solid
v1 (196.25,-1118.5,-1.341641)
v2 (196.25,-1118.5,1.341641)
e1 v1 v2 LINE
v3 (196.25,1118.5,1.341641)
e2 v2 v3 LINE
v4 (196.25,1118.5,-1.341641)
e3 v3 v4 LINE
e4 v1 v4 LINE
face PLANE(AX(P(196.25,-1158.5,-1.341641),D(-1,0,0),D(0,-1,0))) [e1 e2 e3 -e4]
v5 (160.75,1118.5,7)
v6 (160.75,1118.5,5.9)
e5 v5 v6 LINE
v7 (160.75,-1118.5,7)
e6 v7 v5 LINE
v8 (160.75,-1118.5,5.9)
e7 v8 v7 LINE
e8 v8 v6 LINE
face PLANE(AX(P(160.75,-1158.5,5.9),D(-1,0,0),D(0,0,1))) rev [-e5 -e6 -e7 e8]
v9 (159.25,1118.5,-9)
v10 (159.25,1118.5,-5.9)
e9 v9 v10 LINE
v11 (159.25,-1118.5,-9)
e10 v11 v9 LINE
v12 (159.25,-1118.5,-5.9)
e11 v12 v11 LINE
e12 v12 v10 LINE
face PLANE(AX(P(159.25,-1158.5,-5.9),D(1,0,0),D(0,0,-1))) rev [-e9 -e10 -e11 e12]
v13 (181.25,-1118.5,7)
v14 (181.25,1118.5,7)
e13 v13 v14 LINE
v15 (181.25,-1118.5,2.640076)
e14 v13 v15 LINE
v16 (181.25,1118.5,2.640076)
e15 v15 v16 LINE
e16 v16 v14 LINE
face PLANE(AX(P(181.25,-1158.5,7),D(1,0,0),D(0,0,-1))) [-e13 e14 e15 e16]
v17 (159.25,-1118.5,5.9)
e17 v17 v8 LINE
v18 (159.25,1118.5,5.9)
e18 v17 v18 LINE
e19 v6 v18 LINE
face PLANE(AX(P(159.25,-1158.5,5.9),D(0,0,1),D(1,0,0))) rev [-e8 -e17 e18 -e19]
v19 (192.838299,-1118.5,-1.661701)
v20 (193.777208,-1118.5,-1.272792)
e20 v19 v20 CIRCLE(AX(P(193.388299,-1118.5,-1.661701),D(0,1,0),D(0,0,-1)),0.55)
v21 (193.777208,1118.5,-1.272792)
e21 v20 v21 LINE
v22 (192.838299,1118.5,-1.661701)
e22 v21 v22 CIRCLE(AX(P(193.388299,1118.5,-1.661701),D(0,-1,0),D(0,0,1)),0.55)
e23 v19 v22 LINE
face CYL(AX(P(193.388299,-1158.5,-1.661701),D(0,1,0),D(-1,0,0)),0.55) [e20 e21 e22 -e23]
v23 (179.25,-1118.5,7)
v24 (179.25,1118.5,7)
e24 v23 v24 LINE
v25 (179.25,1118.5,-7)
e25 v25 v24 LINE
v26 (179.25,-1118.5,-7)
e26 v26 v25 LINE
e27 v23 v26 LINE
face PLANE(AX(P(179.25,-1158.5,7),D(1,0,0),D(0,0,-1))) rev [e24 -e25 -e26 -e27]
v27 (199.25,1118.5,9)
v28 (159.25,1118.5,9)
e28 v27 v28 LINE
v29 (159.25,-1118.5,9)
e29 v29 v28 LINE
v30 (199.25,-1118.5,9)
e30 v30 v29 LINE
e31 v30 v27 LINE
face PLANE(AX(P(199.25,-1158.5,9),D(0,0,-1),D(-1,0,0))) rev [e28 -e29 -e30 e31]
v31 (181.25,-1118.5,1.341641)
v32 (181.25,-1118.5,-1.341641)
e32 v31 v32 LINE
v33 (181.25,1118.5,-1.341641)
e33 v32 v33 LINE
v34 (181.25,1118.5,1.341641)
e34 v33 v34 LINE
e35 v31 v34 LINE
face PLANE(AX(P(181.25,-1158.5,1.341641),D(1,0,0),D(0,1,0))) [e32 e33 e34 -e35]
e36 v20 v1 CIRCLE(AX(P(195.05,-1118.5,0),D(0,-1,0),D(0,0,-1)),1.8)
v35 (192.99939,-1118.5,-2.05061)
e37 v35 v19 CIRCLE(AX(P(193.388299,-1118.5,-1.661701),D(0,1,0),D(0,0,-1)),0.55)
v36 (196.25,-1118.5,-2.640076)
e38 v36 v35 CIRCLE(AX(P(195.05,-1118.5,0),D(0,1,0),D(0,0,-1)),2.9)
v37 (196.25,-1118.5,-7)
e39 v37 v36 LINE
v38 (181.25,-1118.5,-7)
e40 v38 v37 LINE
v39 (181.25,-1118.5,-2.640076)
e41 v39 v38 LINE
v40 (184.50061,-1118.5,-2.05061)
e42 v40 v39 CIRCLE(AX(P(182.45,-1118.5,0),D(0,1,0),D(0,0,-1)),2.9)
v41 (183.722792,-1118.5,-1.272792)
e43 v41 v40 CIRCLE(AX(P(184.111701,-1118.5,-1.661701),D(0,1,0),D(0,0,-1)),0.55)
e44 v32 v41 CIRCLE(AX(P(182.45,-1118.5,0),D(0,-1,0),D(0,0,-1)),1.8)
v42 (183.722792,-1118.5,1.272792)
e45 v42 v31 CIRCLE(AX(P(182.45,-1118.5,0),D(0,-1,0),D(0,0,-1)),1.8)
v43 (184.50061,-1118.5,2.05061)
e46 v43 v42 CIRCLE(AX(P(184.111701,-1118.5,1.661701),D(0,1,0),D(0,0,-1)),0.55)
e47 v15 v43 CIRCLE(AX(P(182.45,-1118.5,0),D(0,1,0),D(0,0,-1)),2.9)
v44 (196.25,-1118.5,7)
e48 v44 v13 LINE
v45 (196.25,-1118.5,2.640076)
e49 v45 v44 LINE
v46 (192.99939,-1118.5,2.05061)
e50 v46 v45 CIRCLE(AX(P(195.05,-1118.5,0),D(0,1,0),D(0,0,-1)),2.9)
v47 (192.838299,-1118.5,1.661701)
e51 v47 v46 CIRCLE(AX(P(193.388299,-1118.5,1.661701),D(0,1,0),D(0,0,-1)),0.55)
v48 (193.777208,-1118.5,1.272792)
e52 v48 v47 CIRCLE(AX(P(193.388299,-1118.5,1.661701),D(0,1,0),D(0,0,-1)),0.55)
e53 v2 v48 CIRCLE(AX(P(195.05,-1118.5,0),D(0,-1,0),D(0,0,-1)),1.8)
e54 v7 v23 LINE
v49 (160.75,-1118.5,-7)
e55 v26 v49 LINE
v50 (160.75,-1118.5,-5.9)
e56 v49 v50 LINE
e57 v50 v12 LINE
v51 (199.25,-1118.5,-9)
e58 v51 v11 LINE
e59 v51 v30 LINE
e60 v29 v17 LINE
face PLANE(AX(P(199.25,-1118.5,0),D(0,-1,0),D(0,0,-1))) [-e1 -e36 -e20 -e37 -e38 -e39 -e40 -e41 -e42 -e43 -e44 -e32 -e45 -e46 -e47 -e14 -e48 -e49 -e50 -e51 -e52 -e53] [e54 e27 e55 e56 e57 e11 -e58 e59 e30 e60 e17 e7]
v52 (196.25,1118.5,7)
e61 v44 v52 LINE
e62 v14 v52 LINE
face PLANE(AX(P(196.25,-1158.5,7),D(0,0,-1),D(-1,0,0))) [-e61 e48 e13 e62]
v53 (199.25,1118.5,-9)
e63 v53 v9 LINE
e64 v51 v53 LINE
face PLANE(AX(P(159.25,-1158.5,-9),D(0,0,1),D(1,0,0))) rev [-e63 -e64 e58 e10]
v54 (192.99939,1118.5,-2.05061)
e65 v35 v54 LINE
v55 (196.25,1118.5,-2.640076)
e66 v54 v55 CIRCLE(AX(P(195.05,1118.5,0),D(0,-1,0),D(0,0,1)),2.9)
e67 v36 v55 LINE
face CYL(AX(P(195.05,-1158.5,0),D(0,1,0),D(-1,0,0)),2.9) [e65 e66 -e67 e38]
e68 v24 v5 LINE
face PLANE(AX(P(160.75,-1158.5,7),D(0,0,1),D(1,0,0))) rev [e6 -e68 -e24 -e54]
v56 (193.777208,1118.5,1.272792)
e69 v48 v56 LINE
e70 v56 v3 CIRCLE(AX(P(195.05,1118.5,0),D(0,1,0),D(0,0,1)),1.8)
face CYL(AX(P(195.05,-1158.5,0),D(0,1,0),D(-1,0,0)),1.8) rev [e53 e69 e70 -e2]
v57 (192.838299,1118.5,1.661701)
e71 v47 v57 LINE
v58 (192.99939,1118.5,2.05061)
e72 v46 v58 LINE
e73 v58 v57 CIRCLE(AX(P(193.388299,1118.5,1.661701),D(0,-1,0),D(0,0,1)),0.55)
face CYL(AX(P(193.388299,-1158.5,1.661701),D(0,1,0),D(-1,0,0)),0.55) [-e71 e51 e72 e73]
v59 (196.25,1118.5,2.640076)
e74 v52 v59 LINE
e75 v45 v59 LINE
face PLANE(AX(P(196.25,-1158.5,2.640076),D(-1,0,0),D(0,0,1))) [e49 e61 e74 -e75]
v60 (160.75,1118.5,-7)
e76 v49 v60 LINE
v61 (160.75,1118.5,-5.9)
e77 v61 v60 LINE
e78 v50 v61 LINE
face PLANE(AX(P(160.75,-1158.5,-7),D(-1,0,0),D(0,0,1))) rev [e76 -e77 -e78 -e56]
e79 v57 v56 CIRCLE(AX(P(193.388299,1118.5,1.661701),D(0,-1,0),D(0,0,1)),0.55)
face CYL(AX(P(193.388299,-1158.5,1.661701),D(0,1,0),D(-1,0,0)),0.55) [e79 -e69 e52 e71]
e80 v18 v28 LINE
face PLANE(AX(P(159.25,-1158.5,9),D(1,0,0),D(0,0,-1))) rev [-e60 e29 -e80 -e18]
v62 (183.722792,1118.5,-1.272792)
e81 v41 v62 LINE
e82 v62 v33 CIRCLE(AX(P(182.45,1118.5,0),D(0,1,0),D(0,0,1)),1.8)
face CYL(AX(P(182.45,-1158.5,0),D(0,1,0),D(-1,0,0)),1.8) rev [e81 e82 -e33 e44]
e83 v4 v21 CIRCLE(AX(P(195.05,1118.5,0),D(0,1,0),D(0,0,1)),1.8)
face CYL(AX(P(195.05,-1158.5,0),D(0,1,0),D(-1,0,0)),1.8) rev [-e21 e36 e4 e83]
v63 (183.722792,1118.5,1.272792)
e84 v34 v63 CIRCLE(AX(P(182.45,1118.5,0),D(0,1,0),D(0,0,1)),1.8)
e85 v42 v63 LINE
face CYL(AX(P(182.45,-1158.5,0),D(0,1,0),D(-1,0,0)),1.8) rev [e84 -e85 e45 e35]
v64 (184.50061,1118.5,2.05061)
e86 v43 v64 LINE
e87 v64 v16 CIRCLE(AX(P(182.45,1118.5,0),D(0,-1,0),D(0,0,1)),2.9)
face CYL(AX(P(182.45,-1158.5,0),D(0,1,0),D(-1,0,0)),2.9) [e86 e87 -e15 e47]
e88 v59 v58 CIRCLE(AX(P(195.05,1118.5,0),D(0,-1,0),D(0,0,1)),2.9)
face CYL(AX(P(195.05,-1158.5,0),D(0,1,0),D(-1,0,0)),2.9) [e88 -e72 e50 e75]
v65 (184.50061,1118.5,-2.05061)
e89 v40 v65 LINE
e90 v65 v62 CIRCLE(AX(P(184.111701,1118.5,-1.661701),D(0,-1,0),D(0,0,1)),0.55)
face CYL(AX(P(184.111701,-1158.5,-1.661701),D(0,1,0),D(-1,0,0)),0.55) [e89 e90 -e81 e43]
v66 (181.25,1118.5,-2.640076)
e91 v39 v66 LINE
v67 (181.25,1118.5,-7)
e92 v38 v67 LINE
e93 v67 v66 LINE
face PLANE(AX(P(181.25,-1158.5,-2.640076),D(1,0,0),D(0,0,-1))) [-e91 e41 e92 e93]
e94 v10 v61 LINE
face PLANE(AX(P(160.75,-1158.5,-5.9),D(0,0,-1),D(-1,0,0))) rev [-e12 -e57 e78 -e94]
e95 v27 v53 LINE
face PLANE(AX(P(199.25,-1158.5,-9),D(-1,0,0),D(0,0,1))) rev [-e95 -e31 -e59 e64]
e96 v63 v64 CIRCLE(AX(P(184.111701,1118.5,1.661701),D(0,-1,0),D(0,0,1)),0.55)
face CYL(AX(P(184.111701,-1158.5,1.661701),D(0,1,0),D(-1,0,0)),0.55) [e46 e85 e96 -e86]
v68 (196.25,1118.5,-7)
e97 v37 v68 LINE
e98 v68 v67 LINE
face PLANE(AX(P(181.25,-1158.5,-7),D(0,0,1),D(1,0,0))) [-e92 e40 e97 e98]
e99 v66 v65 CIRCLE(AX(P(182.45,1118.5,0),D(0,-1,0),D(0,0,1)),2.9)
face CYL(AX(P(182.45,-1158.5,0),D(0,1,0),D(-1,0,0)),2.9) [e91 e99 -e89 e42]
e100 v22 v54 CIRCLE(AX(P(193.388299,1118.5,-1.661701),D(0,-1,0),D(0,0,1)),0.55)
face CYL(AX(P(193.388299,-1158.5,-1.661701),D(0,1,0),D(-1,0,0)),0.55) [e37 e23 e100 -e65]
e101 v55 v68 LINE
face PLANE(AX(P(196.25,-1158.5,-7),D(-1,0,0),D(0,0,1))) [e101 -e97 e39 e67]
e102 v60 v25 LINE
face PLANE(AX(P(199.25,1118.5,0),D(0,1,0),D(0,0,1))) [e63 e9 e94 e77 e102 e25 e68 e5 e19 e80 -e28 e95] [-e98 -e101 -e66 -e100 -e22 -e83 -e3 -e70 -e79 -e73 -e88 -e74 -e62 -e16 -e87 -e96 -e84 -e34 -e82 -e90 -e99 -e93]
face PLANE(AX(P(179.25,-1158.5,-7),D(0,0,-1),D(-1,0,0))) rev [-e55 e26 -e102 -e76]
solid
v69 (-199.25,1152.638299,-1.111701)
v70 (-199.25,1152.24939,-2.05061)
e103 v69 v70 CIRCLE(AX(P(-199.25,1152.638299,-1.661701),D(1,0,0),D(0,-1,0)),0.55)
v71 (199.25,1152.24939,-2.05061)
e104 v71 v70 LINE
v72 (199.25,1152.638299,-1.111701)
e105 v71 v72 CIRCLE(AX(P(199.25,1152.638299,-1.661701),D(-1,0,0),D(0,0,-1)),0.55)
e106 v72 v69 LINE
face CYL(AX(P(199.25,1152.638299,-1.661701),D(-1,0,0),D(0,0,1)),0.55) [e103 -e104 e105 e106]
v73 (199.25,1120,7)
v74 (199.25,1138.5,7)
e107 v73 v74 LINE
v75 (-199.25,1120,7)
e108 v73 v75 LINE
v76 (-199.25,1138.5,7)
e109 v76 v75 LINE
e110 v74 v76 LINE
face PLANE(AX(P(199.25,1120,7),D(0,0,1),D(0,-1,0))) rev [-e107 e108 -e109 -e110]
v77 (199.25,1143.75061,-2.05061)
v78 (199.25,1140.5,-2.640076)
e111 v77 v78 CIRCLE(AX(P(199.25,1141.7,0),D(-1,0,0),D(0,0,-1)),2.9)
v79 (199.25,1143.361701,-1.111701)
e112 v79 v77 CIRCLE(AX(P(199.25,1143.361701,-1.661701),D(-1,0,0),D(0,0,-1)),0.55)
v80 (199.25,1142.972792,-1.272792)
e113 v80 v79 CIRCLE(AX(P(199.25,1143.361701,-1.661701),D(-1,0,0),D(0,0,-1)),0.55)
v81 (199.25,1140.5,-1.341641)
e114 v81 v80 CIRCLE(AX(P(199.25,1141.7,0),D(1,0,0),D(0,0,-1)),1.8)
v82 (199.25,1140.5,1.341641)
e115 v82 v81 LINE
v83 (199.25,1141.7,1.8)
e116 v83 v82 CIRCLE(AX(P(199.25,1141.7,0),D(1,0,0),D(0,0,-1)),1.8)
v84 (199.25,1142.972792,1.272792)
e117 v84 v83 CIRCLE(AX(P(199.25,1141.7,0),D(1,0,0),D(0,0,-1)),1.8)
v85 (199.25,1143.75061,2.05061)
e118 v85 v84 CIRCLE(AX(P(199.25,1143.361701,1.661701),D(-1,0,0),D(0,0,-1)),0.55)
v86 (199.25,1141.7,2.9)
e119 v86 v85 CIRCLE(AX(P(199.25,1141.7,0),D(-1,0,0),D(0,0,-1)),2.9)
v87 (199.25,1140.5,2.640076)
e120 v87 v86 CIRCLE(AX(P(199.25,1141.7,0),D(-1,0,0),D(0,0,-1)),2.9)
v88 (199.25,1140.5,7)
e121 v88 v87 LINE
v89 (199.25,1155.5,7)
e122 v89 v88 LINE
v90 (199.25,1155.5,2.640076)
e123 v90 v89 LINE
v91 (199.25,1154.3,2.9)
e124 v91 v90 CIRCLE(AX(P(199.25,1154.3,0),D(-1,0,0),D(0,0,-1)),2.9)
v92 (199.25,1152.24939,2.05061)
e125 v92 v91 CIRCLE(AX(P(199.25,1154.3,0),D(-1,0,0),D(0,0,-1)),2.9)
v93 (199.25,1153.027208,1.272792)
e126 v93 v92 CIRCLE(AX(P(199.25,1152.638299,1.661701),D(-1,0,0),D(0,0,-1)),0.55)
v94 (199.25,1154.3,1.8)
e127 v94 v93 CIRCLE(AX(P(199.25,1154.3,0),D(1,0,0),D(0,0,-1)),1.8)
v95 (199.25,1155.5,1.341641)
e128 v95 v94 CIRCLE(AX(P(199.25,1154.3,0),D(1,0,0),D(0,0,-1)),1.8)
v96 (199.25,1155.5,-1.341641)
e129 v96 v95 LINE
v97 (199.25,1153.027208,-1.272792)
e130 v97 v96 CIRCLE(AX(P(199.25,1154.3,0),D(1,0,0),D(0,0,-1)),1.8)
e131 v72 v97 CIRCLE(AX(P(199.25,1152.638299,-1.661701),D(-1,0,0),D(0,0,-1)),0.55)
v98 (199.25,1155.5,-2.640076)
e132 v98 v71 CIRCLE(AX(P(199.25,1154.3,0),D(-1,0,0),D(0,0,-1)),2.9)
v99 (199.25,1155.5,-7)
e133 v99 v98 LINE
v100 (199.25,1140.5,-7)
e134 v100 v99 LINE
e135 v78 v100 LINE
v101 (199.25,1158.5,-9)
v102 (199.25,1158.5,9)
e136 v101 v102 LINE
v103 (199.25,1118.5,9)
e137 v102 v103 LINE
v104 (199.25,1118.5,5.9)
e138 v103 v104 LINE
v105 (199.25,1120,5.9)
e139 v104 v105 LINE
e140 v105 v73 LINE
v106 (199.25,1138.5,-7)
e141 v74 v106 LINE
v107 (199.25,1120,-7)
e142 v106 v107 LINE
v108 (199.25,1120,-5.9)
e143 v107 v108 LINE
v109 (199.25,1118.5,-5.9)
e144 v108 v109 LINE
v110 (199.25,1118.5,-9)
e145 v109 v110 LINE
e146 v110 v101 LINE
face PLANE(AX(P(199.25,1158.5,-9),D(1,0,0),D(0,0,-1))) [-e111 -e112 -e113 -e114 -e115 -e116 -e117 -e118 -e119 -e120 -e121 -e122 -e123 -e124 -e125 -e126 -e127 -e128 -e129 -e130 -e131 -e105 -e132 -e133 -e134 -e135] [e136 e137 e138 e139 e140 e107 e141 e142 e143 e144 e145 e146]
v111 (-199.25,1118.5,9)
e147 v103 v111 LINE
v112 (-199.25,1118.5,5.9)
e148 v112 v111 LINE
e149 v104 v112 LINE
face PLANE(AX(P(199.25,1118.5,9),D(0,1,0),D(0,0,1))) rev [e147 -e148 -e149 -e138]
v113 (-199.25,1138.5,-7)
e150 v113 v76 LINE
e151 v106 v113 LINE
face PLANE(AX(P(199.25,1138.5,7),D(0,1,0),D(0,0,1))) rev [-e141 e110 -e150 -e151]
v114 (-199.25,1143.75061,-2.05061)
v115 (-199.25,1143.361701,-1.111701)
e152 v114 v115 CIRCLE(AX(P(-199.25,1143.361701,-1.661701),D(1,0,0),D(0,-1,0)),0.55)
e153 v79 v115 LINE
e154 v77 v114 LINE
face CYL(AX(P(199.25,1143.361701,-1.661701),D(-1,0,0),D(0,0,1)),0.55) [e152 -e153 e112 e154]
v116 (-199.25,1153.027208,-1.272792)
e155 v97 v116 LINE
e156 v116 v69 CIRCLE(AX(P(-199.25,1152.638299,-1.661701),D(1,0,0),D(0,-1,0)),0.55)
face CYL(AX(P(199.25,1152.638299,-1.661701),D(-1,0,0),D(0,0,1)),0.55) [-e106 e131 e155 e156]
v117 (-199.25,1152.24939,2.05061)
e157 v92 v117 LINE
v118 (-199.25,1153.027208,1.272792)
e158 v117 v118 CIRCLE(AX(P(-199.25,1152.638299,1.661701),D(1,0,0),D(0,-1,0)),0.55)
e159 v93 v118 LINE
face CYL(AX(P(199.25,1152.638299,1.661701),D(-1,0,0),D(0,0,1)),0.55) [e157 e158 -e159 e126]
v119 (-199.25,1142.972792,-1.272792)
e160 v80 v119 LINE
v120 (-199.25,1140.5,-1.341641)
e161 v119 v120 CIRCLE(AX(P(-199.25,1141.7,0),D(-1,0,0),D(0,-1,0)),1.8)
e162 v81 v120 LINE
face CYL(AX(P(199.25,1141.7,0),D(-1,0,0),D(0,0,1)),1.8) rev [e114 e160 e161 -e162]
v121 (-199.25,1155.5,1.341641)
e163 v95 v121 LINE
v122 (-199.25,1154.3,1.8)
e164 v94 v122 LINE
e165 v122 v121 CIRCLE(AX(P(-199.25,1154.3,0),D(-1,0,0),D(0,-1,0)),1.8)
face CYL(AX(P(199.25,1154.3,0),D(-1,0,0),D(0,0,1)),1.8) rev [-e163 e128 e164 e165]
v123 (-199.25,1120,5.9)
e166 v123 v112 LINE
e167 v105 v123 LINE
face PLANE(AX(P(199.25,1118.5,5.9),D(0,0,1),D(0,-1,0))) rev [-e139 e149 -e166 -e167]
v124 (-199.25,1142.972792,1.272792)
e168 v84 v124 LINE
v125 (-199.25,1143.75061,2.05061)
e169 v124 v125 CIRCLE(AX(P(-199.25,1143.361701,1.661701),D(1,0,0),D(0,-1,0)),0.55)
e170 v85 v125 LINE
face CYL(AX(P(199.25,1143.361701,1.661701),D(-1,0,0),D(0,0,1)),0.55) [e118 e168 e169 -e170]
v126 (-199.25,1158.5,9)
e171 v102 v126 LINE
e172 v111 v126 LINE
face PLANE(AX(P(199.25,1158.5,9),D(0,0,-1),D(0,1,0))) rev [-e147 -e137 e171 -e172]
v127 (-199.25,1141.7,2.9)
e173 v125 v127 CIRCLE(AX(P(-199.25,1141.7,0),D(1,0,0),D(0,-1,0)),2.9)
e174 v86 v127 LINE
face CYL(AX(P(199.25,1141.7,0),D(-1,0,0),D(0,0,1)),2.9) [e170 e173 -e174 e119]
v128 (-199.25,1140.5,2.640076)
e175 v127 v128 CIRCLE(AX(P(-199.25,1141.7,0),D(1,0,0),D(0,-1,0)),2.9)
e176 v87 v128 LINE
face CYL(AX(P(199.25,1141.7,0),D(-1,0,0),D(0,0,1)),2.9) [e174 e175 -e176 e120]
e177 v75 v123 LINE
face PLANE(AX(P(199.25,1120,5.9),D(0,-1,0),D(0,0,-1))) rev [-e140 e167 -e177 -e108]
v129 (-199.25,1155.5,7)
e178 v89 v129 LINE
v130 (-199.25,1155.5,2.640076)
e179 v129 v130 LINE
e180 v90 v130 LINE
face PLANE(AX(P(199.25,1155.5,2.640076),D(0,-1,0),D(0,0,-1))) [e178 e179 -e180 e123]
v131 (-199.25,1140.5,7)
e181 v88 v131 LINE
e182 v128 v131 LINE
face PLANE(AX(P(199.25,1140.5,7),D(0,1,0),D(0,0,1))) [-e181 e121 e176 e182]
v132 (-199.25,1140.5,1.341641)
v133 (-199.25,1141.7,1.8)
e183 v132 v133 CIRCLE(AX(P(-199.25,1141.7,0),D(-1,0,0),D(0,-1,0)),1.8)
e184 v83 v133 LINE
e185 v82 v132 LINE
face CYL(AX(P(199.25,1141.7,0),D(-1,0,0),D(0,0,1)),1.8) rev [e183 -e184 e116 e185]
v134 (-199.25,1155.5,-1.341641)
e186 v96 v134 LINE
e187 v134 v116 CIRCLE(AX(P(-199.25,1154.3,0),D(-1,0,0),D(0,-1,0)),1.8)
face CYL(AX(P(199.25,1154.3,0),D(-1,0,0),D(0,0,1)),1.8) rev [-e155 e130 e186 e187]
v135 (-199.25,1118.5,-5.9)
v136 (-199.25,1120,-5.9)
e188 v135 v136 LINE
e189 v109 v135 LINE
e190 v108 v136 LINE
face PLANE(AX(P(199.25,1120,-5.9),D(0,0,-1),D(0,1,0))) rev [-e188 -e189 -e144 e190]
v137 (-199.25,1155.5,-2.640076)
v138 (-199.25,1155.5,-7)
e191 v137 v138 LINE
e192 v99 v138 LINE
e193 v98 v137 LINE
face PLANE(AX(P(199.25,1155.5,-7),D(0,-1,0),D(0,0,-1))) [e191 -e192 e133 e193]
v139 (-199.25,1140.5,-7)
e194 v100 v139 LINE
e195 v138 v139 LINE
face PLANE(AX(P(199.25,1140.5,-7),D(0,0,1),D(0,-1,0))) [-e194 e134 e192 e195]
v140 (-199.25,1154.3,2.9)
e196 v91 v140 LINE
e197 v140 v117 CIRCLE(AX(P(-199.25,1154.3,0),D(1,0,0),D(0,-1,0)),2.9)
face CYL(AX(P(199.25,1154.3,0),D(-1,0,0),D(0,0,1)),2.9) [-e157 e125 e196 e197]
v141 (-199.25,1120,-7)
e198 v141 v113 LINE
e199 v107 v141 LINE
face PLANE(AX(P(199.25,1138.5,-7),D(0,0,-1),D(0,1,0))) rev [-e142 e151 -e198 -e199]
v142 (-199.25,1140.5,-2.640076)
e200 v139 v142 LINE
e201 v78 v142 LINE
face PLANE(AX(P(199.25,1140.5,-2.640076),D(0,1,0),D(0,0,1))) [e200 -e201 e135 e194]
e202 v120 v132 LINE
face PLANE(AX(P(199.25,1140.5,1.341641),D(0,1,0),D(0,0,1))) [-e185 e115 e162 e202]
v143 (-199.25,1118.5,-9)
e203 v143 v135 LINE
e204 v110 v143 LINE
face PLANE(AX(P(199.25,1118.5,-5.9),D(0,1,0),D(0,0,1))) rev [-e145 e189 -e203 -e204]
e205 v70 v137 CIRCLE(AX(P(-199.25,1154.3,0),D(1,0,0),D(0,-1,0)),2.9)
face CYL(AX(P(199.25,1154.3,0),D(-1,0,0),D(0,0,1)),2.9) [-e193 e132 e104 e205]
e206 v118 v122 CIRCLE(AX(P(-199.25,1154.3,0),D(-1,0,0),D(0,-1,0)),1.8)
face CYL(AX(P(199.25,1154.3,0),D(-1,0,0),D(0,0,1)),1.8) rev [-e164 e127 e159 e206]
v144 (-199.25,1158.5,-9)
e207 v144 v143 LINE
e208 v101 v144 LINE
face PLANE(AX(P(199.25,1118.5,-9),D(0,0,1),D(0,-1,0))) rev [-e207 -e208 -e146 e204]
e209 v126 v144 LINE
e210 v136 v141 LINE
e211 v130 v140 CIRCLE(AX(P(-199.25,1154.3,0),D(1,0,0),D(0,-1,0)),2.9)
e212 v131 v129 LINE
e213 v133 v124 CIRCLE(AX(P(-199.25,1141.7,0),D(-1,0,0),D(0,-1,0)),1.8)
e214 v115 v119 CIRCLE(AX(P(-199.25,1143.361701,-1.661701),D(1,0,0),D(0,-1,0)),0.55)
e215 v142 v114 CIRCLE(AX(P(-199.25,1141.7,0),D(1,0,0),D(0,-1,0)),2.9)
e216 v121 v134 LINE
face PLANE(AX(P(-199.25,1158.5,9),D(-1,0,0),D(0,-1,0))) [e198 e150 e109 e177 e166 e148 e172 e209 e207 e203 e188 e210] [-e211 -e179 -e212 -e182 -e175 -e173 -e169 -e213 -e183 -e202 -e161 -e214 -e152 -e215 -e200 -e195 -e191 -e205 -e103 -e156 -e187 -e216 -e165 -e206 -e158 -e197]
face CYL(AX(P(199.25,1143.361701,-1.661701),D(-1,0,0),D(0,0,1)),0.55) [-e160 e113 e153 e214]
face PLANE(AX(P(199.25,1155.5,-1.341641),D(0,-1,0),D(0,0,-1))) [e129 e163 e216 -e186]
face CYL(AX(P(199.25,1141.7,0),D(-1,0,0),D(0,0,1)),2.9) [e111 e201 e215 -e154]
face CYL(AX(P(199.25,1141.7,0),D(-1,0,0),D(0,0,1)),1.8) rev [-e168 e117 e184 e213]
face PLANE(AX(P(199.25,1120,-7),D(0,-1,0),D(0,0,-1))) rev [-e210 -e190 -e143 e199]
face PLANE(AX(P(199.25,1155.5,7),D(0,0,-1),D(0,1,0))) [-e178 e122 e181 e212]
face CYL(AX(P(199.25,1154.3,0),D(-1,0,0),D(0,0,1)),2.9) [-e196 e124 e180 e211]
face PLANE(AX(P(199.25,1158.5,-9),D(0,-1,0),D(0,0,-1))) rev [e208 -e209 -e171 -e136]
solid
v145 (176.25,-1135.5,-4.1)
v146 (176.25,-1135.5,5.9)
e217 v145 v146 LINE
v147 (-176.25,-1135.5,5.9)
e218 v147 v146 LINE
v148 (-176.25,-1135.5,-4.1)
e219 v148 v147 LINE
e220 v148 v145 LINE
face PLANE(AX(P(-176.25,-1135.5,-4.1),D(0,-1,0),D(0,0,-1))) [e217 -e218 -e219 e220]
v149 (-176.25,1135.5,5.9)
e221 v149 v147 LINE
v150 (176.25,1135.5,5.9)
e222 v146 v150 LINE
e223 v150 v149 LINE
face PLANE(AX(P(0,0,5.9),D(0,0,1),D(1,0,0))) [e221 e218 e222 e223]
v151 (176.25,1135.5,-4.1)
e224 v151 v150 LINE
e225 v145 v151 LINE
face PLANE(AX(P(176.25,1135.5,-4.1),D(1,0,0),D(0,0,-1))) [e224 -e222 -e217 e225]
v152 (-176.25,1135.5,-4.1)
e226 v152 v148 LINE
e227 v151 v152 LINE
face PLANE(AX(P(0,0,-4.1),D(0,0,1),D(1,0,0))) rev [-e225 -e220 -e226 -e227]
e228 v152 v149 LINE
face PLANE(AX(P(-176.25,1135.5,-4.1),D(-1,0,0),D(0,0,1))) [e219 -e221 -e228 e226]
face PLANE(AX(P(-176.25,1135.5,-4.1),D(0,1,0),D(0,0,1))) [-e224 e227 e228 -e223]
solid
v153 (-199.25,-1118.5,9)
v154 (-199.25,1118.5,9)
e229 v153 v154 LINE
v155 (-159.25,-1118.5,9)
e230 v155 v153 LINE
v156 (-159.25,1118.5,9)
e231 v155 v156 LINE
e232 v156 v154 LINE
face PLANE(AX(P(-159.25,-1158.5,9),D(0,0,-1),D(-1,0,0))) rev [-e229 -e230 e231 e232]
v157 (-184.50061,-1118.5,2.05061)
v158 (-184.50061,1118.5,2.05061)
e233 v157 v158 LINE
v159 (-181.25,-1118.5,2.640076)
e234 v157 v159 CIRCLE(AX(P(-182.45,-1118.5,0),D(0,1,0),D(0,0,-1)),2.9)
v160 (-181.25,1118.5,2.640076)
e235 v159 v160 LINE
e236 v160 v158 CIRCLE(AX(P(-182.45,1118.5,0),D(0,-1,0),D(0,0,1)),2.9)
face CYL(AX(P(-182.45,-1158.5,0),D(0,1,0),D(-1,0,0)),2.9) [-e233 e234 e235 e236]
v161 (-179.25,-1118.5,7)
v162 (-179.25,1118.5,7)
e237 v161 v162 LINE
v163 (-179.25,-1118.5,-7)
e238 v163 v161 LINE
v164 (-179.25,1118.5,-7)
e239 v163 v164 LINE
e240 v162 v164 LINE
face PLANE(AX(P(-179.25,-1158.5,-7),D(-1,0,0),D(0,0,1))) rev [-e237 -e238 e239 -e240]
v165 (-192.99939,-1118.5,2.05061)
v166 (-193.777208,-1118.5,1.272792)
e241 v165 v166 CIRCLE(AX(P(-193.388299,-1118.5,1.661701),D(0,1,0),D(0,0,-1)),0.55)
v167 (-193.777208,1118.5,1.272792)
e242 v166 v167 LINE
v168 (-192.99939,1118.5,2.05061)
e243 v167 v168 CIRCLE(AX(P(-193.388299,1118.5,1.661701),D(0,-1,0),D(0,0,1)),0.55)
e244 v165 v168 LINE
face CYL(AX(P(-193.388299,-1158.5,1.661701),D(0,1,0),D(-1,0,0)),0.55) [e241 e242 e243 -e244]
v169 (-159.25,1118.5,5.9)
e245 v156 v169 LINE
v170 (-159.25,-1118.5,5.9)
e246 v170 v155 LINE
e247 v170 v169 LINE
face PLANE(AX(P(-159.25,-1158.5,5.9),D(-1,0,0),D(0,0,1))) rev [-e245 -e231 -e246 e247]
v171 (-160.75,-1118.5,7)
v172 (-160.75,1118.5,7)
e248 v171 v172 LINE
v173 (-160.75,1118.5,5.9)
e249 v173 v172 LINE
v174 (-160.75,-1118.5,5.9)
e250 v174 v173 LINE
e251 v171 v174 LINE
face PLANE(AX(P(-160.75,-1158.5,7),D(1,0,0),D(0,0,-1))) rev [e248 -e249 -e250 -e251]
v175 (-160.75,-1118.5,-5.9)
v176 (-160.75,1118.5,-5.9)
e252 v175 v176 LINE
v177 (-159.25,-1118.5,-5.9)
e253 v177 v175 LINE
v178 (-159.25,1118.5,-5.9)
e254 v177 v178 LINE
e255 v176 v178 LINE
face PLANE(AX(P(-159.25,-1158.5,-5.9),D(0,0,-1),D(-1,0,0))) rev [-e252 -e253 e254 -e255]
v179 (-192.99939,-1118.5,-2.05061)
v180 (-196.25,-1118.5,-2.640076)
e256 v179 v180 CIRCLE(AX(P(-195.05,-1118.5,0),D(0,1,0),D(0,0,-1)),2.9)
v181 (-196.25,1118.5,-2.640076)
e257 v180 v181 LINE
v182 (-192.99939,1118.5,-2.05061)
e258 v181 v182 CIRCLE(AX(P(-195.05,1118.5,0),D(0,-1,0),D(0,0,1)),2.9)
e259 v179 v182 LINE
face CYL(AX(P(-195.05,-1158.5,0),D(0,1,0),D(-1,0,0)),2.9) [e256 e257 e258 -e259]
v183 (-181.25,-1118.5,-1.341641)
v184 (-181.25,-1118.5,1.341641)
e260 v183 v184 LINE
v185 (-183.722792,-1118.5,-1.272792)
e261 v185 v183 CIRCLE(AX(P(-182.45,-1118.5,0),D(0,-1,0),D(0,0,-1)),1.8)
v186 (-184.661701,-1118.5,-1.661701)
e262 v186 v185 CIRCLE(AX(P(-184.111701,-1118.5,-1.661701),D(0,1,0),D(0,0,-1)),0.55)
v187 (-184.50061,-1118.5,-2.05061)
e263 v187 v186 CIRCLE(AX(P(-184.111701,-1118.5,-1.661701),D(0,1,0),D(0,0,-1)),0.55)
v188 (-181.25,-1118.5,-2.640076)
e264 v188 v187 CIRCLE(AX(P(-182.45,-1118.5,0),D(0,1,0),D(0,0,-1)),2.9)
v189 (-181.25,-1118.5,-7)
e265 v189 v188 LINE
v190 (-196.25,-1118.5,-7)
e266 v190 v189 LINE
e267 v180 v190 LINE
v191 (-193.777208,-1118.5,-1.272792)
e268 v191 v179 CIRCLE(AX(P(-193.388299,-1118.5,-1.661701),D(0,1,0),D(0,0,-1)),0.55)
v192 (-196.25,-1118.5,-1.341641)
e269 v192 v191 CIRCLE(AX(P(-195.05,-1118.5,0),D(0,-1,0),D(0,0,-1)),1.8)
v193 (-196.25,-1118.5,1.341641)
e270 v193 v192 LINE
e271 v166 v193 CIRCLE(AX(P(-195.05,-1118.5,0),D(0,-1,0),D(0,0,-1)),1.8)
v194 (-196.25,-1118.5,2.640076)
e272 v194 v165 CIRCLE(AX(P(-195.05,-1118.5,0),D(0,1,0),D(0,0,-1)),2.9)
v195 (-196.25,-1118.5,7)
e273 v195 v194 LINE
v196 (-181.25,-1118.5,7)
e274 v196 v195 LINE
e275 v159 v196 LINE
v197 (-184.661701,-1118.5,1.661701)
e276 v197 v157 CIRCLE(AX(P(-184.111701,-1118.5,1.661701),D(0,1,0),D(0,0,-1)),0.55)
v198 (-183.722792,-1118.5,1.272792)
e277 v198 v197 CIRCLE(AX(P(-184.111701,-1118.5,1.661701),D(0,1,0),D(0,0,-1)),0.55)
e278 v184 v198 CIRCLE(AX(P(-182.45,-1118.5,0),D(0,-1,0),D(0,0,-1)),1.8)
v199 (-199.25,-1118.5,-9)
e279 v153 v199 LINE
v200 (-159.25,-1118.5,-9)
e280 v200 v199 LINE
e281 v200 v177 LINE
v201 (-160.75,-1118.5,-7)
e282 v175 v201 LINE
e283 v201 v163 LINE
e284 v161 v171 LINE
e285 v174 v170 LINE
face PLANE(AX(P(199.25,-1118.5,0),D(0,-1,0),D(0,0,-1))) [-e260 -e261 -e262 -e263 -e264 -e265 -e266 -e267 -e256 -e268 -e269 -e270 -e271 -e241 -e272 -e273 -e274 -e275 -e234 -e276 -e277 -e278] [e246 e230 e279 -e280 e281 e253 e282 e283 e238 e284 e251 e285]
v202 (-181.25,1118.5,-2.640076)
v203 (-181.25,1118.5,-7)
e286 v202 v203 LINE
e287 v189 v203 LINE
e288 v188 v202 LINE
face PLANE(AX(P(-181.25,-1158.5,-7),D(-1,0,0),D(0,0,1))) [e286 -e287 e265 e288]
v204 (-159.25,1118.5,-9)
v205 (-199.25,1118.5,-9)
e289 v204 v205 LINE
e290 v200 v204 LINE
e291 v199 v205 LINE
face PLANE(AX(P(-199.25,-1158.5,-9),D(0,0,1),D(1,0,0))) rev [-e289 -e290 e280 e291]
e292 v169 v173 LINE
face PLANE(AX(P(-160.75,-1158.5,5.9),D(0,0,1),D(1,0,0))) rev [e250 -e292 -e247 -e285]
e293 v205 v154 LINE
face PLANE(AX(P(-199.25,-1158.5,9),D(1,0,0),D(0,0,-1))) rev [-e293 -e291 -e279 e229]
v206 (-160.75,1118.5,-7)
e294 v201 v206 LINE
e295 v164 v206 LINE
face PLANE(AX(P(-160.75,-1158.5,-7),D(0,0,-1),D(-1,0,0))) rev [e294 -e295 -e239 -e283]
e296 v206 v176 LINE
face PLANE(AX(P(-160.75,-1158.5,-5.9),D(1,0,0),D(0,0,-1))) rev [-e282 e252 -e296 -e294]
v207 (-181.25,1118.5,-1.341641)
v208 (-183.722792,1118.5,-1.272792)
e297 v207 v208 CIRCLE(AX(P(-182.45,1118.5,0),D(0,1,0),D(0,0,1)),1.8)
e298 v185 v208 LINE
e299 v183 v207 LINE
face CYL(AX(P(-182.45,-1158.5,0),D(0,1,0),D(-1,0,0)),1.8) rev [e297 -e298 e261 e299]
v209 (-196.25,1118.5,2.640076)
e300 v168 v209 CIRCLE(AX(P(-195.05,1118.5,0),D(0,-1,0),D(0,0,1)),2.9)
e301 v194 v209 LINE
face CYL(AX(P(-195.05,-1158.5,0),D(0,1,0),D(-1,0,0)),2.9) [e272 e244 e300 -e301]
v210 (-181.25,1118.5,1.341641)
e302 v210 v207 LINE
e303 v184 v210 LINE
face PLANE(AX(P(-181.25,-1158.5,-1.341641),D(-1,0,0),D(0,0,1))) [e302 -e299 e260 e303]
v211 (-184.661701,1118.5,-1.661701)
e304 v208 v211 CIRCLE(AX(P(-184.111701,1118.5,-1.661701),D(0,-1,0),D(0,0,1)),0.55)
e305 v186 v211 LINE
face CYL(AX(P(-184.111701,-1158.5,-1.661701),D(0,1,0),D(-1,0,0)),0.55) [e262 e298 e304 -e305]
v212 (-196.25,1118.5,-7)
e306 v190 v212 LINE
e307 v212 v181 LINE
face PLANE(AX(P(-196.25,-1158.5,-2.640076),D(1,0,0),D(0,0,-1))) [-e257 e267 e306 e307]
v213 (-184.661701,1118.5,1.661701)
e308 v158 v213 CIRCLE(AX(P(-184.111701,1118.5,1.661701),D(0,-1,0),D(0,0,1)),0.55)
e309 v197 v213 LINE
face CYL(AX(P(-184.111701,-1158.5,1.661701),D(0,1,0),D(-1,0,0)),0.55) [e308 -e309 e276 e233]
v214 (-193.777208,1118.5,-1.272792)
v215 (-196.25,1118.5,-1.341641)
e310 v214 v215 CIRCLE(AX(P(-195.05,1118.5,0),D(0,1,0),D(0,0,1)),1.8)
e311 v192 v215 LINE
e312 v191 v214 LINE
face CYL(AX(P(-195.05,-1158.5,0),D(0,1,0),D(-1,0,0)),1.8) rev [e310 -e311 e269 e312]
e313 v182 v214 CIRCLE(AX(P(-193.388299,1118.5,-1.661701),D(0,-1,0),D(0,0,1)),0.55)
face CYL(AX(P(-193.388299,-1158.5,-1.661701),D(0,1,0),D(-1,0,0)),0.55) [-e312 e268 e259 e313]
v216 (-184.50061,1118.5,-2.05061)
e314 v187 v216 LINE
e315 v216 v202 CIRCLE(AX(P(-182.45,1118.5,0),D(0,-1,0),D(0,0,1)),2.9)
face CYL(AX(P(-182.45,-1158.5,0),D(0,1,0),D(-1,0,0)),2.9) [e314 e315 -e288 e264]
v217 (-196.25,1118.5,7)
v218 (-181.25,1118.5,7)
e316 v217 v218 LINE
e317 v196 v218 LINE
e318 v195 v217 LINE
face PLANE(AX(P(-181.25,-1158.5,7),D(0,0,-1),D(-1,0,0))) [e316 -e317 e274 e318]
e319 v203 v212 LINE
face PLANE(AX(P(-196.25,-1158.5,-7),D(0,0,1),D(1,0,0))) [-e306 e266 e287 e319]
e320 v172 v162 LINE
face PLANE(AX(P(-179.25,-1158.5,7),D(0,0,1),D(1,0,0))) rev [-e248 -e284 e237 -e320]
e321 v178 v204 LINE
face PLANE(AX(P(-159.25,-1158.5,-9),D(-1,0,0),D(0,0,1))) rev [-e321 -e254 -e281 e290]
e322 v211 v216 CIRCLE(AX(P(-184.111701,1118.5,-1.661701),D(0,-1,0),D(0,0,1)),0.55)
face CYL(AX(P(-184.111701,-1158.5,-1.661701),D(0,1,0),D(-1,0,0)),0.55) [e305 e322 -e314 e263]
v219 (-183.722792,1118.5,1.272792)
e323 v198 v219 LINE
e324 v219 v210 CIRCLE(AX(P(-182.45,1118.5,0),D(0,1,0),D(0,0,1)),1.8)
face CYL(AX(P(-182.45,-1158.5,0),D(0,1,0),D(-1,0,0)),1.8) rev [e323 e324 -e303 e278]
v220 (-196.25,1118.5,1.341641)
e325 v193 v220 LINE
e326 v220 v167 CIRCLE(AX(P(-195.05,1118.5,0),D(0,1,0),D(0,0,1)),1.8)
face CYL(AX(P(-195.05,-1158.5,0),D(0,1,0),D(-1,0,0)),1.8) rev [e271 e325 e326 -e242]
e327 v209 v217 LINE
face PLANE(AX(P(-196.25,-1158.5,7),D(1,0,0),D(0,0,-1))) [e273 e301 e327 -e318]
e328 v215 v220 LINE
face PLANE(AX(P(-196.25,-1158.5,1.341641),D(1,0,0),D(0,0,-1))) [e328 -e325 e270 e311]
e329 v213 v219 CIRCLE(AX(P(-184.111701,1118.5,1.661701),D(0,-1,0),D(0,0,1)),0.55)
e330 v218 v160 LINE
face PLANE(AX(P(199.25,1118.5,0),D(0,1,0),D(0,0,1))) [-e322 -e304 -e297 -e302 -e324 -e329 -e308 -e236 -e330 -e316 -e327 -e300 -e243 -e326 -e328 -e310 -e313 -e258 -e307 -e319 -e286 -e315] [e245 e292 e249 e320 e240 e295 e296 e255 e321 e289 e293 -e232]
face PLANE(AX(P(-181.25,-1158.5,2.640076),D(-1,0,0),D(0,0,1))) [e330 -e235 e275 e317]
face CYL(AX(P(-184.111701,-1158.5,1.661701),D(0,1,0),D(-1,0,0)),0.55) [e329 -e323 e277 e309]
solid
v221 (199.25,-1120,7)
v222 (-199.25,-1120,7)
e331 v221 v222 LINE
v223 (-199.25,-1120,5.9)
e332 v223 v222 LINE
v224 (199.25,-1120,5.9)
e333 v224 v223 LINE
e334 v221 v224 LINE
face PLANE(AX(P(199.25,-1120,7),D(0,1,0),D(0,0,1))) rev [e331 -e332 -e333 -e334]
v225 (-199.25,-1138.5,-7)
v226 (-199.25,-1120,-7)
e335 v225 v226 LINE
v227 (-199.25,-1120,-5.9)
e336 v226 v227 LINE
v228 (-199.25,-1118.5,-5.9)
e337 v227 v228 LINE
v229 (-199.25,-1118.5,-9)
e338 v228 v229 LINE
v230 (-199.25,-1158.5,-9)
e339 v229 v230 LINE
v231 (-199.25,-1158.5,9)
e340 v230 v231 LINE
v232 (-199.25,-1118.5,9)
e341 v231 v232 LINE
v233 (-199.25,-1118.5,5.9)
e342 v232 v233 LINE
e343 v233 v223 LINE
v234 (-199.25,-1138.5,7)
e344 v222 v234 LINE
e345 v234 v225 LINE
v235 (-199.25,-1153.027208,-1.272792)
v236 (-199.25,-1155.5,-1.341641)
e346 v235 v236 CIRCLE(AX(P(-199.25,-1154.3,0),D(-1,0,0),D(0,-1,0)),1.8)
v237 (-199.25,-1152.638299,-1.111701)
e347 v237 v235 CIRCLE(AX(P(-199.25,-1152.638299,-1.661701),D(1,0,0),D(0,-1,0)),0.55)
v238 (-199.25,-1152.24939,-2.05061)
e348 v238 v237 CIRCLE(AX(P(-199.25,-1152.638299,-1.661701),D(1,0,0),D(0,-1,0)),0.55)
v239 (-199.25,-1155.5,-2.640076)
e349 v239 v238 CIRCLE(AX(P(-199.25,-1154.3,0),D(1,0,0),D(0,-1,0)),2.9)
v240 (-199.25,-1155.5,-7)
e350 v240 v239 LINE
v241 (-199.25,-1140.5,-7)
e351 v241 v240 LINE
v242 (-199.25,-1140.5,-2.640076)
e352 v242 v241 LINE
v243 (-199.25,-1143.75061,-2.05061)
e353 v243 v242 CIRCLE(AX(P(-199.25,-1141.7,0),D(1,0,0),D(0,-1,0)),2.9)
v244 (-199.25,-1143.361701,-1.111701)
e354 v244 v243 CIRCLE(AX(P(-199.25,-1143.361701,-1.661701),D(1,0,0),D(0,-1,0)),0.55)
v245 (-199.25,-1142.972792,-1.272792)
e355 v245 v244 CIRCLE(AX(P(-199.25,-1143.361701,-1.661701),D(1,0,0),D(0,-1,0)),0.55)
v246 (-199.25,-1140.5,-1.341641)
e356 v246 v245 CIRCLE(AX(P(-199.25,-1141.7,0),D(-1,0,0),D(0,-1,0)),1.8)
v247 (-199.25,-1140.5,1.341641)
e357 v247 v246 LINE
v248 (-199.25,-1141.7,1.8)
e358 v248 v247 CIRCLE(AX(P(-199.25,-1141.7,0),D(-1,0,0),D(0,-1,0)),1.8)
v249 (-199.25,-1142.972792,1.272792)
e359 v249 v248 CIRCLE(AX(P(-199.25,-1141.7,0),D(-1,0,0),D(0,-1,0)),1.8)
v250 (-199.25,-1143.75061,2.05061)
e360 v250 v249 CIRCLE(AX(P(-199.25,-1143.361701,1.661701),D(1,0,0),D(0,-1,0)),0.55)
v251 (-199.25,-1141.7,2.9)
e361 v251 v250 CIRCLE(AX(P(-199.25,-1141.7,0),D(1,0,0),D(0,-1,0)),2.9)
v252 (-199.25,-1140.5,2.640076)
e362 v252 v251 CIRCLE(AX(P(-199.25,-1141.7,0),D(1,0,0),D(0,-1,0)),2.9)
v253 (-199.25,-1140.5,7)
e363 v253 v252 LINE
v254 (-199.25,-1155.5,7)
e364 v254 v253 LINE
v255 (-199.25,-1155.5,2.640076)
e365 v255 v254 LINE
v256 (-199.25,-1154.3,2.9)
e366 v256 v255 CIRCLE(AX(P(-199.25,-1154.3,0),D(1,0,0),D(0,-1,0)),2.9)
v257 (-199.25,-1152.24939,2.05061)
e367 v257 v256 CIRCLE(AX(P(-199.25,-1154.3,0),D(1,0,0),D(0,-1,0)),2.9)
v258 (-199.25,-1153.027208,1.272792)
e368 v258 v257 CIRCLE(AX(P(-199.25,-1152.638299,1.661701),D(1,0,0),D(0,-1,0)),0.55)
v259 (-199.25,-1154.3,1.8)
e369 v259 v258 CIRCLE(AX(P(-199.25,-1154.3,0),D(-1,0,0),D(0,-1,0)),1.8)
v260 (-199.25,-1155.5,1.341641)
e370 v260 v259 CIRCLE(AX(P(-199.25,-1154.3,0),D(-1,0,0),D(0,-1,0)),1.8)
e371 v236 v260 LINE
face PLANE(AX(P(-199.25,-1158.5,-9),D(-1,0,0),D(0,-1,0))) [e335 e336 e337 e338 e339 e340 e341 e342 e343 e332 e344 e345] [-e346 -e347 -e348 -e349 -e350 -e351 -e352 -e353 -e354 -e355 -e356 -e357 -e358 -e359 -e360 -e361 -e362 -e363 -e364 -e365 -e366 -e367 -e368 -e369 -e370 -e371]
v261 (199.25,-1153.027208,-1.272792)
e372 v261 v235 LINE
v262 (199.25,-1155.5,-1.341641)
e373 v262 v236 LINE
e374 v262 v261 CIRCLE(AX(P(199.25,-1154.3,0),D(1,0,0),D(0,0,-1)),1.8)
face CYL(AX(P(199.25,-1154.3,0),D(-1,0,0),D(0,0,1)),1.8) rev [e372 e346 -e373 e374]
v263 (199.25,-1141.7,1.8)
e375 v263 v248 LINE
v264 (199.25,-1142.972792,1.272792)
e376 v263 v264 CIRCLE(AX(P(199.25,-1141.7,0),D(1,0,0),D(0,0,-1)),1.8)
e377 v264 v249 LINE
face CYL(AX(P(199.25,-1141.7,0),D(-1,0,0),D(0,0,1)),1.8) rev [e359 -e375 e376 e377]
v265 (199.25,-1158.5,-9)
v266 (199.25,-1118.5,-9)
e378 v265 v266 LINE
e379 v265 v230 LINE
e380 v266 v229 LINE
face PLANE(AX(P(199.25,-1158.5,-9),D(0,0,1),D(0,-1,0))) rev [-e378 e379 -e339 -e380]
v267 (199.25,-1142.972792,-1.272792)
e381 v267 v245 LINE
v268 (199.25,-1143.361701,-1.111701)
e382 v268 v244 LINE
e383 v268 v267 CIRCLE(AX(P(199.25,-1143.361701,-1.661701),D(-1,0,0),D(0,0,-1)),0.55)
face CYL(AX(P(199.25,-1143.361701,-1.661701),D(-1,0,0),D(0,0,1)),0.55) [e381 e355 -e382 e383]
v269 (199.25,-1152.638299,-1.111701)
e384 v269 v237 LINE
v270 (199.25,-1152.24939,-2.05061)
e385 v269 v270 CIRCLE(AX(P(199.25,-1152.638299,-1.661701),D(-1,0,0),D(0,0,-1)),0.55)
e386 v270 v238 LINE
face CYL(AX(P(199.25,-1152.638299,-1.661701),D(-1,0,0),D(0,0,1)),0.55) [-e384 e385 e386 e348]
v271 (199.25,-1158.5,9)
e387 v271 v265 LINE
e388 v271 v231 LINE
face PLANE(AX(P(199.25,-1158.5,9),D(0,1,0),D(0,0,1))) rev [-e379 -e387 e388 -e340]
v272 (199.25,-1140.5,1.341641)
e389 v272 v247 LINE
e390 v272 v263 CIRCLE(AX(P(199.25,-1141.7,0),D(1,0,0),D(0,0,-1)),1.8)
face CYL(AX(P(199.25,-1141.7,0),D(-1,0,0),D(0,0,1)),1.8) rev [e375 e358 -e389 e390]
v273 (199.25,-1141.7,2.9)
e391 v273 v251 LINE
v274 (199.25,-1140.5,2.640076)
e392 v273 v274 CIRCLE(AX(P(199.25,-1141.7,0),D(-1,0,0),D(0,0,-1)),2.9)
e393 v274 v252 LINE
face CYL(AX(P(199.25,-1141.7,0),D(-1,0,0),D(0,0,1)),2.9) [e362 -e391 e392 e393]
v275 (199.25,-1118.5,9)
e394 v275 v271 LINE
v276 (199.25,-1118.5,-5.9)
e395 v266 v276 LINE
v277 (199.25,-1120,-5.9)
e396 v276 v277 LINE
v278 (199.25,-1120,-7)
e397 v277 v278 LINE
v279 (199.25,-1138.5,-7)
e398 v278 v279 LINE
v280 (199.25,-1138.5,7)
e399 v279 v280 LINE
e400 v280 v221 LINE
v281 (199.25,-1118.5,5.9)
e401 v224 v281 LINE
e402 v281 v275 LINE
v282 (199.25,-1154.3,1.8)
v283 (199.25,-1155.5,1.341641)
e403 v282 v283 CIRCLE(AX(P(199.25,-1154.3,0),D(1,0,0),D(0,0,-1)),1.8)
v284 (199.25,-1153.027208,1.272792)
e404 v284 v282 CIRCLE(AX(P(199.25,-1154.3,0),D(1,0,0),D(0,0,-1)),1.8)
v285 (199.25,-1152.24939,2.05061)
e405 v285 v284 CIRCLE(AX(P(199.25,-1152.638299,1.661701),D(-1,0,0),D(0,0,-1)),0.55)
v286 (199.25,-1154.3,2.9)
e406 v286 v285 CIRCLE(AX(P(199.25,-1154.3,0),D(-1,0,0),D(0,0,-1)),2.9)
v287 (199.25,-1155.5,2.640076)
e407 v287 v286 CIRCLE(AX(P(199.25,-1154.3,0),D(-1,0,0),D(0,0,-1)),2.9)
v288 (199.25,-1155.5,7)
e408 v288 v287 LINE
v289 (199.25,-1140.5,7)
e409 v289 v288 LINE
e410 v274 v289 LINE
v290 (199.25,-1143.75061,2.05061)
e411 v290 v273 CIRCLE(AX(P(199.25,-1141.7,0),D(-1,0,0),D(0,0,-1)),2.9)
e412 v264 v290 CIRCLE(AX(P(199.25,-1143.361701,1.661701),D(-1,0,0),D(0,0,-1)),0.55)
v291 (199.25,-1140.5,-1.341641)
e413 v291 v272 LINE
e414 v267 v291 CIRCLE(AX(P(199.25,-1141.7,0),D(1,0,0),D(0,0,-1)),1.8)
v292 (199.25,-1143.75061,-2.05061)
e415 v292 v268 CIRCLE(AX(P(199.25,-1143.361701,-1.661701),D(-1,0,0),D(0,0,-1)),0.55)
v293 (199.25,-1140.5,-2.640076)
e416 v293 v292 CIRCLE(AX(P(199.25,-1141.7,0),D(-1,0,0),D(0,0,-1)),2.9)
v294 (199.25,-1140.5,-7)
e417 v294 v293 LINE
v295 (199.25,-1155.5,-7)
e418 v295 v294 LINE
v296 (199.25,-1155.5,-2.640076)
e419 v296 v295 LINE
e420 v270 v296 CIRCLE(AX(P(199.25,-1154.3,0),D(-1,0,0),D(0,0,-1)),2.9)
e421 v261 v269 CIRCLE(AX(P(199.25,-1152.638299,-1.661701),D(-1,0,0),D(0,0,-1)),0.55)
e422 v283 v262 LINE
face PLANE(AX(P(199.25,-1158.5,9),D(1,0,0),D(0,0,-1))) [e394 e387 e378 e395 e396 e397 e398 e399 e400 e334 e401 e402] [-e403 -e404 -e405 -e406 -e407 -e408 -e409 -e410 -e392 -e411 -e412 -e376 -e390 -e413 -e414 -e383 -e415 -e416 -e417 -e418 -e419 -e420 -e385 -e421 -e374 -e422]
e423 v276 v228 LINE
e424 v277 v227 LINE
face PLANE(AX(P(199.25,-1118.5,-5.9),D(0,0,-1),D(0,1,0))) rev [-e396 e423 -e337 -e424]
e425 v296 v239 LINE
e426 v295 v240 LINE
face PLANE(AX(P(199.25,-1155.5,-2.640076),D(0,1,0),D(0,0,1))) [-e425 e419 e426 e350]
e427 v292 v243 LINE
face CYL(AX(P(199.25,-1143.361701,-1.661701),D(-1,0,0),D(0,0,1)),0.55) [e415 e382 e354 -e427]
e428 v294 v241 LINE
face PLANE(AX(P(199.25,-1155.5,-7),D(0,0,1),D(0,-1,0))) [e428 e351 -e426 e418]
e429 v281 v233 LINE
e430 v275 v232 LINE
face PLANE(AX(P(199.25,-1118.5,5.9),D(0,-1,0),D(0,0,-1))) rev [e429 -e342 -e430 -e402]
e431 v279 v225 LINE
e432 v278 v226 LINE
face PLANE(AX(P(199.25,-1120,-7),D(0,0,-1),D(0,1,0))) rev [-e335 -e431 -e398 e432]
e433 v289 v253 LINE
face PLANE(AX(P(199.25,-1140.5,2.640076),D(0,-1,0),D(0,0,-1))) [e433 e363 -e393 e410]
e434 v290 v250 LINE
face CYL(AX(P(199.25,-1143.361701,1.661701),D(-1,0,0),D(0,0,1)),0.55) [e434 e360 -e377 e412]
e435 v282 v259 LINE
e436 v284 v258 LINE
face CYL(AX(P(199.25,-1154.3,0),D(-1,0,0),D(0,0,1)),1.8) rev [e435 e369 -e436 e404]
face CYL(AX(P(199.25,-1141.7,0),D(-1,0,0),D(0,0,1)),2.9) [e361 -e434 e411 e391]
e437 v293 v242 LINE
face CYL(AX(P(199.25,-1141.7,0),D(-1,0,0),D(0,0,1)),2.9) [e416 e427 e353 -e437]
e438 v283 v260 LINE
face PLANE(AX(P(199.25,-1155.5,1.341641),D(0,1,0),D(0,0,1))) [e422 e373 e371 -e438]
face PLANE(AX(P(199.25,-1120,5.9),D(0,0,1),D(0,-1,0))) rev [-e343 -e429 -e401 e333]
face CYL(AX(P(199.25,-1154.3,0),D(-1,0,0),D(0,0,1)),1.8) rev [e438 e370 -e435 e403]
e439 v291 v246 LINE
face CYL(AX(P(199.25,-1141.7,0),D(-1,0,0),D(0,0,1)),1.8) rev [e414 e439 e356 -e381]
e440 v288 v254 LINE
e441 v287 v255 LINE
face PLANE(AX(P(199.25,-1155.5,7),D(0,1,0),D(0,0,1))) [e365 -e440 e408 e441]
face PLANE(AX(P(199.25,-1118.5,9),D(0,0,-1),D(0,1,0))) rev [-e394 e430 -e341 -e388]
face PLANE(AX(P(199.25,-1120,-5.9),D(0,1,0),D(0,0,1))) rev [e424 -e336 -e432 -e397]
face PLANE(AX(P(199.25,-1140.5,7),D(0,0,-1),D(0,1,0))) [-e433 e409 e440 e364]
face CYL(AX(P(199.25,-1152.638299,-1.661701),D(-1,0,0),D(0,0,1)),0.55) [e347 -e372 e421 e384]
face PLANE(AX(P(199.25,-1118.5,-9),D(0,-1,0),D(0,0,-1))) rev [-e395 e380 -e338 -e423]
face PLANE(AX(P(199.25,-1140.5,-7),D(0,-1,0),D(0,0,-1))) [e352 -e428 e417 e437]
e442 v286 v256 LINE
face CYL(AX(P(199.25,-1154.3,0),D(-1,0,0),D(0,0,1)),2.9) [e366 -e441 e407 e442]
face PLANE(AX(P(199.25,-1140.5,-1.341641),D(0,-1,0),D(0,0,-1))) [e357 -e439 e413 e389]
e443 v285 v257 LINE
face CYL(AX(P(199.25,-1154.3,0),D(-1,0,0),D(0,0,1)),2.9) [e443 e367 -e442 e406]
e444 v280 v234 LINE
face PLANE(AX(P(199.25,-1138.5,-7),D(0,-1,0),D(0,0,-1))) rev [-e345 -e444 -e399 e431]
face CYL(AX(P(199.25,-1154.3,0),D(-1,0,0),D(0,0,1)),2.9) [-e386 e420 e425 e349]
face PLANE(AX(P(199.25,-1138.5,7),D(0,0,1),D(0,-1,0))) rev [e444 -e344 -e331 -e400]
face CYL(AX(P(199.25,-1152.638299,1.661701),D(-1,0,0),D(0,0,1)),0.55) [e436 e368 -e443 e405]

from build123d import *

# Parameters (mm, degrees)
MEMBER_1_DEPTH   = 398.5
MEMBER_1_2_DEPTH = 398.5
MEMBER_1_3_DEPTH = 2319
MEMBER_1_4_DEPTH = 2319
EXTRUDE_START    = -3.1
SKETCH_2_W       = 352.5
SKETCH_2_H       = 2271
EXTRUDE_1_DEPTH  = 10


with BuildPart() as part:
    # Sketch1 → Member 1 (new body)
    with BuildSketch(Plane(origin=(-199.25, 1158.5, 0), x_dir=(0, 0, -1), z_dir=(1, 0, 0))):
        Polygon((7, -38.5), (5.9, -38.5), (5.9, -40), (7, -40), (9, -40), (9, 0), (-9, 0), (-9, -40), (-7, -40), (-5.9, -40), (-5.9, -38.5), (-7, -38.5), (-7, -20), (7, -20), align=None)
        with BuildLine():
            Line((-1.341640786, -18), (1.341640786, -18))
            ThreePointArc((1.341640786, -18), (1.799302724, -16.749903013), (1.272792206, -15.527207794))
            ThreePointArc((1.272792206, -15.527207794), (1.272792206, -14.749390335), (2.050609665, -14.749390335))
            ThreePointArc((2.050609665, -14.749390335), (2.853462499, -16.282552641), (2.640075756, -18))
            Line((2.640075756, -18), (7, -18))
            Line((7, -18), (7, -3))
            Line((7, -3), (2.640075756, -3))
            ThreePointArc((2.640075756, -3), (2.853462499, -4.717447359), (2.050609665, -6.250609665))
            ThreePointArc((2.050609665, -6.250609665), (1.272792206, -6.250609665), (1.272792206, -5.472792206))
            ThreePointArc((1.272792206, -5.472792206), (1.799302724, -4.250096987), (1.341640786, -3))
            Line((1.341640786, -3), (-1.341640786, -3))
            ThreePointArc((-1.341640786, -3), (-1.799302724, -4.250096987), (-1.272792206, -5.472792206))
            ThreePointArc((-1.272792206, -5.472792206), (-1.272792206, -6.250609665), (-2.050609665, -6.250609665))
            ThreePointArc((-2.050609665, -6.250609665), (-2.853462499, -4.717447359), (-2.640075756, -3))
            Line((-2.640075756, -3), (-7, -3))
            Line((-7, -3), (-7, -18))
            Line((-7, -18), (-2.640075756, -18))
            ThreePointArc((-2.640075756, -18), (-2.853462499, -16.282552641), (-2.050609665, -14.749390335))
            ThreePointArc((-2.050609665, -14.749390335), (-1.272792206, -14.749390335), (-1.272792206, -15.527207794))
            ThreePointArc((-1.272792206, -15.527207794), (-1.799302724, -16.749903013), (-1.341640786, -18))
        make_face(mode=Mode.SUBTRACT)
    extrude(amount=MEMBER_1_DEPTH)


with BuildPart() as body_2:
    # Sketch1 on segment 2 (carried to segment 2) → Member 1 2 (new body)
    with BuildSketch(Plane(origin=(-199.25, -1158.5, 0), x_dir=(0, 0, 1), z_dir=(1, 0, 0))):
        Polygon((7, -38.5), (5.9, -38.5), (5.9, -40), (7, -40), (9, -40), (9, 0), (-9, 0), (-9, -40), (-7, -40), (-5.9, -40), (-5.9, -38.5), (-7, -38.5), (-7, -20), (7, -20), align=None)
        with BuildLine():
            Line((-1.341640786, -18), (1.341640786, -18))
            ThreePointArc((1.341640786, -18), (1.799302724, -16.749903013), (1.272792206, -15.527207794))
            ThreePointArc((1.272792206, -15.527207794), (1.272792206, -14.749390335), (2.050609665, -14.749390335))
            ThreePointArc((2.050609665, -14.749390335), (2.853462499, -16.282552641), (2.640075756, -18))
            Line((2.640075756, -18), (7, -18))
            Line((7, -18), (7, -3))
            Line((7, -3), (2.640075756, -3))
            ThreePointArc((2.640075756, -3), (2.853462499, -4.717447359), (2.050609665, -6.250609665))
            ThreePointArc((2.050609665, -6.250609665), (1.272792206, -6.250609665), (1.272792206, -5.472792206))
            ThreePointArc((1.272792206, -5.472792206), (1.799302724, -4.250096987), (1.341640786, -3))
            Line((1.341640786, -3), (-1.341640786, -3))
            ThreePointArc((-1.341640786, -3), (-1.799302724, -4.250096987), (-1.272792206, -5.472792206))
            ThreePointArc((-1.272792206, -5.472792206), (-1.272792206, -6.250609665), (-2.050609665, -6.250609665))
            ThreePointArc((-2.050609665, -6.250609665), (-2.853462499, -4.717447359), (-2.640075756, -3))
            Line((-2.640075756, -3), (-7, -3))
            Line((-7, -3), (-7, -18))
            Line((-7, -18), (-2.640075756, -18))
            ThreePointArc((-2.640075756, -18), (-2.853462499, -16.282552641), (-2.050609665, -14.749390335))
            ThreePointArc((-2.050609665, -14.749390335), (-1.272792206, -14.749390335), (-1.272792206, -15.527207794))
            ThreePointArc((-1.272792206, -15.527207794), (-1.799302724, -16.749903013), (-1.341640786, -18))
        make_face(mode=Mode.SUBTRACT)
    extrude(amount=MEMBER_1_2_DEPTH)


with BuildPart() as body_3:
    # Sketch1 on segment 3 (carried to segment 3) → Member 1 3 (new body)
    with BuildSketch(Plane(origin=(-199.25, 1159.5, 0), x_dir=(0, 0, 1), z_dir=(0, -1, 0))):
        Polygon((7, -38.5), (5.9, -38.5), (5.9, -40), (7, -40), (9, -40), (9, 0), (-9, 0), (-9, -40), (-7, -40), (-5.9, -40), (-5.9, -38.5), (-7, -38.5), (-7, -20), (7, -20), align=None)
        with BuildLine():
            Line((-1.341640786, -18), (1.341640786, -18))
            ThreePointArc((1.341640786, -18), (1.799302724, -16.749903013), (1.272792206, -15.527207794))
            ThreePointArc((1.272792206, -15.527207794), (1.272792206, -14.749390335), (2.050609665, -14.749390335))
            ThreePointArc((2.050609665, -14.749390335), (2.853462499, -16.282552641), (2.640075756, -18))
            Line((2.640075756, -18), (7, -18))
            Line((7, -18), (7, -3))
            Line((7, -3), (2.640075756, -3))
            ThreePointArc((2.640075756, -3), (2.853462499, -4.717447359), (2.050609665, -6.250609665))
            ThreePointArc((2.050609665, -6.250609665), (1.272792206, -6.250609665), (1.272792206, -5.472792206))
            ThreePointArc((1.272792206, -5.472792206), (1.799302724, -4.250096987), (1.341640786, -3))
            Line((1.341640786, -3), (-1.341640786, -3))
            ThreePointArc((-1.341640786, -3), (-1.799302724, -4.250096987), (-1.272792206, -5.472792206))
            ThreePointArc((-1.272792206, -5.472792206), (-1.272792206, -6.250609665), (-2.050609665, -6.250609665))
            ThreePointArc((-2.050609665, -6.250609665), (-2.853462499, -4.717447359), (-2.640075756, -3))
            Line((-2.640075756, -3), (-7, -3))
            Line((-7, -3), (-7, -18))
            Line((-7, -18), (-2.640075756, -18))
            ThreePointArc((-2.640075756, -18), (-2.853462499, -16.282552641), (-2.050609665, -14.749390335))
            ThreePointArc((-2.050609665, -14.749390335), (-1.272792206, -14.749390335), (-1.272792206, -15.527207794))
            ThreePointArc((-1.272792206, -15.527207794), (-1.799302724, -16.749903013), (-1.341640786, -18))
        make_face(mode=Mode.SUBTRACT)
    extrude(amount=MEMBER_1_3_DEPTH)

    # Member 1 3 end butt 1
    split(bisect_by=Plane(origin=(-199.25, 1118.5, 0), x_dir=(1, 0, 0), z_dir=(0, -1, 0)), keep=Keep.TOP)

    # Member 1 3 end butt 2
    split(bisect_by=Plane(origin=(-199.25, -1118.5, 0), x_dir=(-1, 0, 0), z_dir=(0, 1, 0)), keep=Keep.TOP)


with BuildPart() as body_4:
    # Sketch1 on segment 4 (carried to segment 4) → Member 1 4 (new body)
    with BuildSketch(Plane(origin=(199.25, 1159.5, 0), x_dir=(0, 0, -1), z_dir=(0, -1, 0))):
        Polygon((7, -38.5), (5.9, -38.5), (5.9, -40), (7, -40), (9, -40), (9, 0), (-9, 0), (-9, -40), (-7, -40), (-5.9, -40), (-5.9, -38.5), (-7, -38.5), (-7, -20), (7, -20), align=None)
        with BuildLine():
            Line((-1.341640786, -18), (1.341640786, -18))
            ThreePointArc((1.341640786, -18), (1.799302724, -16.749903013), (1.272792206, -15.527207794))
            ThreePointArc((1.272792206, -15.527207794), (1.272792206, -14.749390335), (2.050609665, -14.749390335))
            ThreePointArc((2.050609665, -14.749390335), (2.853462499, -16.282552641), (2.640075756, -18))
            Line((2.640075756, -18), (7, -18))
            Line((7, -18), (7, -3))
            Line((7, -3), (2.640075756, -3))
            ThreePointArc((2.640075756, -3), (2.853462499, -4.717447359), (2.050609665, -6.250609665))
            ThreePointArc((2.050609665, -6.250609665), (1.272792206, -6.250609665), (1.272792206, -5.472792206))
            ThreePointArc((1.272792206, -5.472792206), (1.799302724, -4.250096987), (1.341640786, -3))
            Line((1.341640786, -3), (-1.341640786, -3))
            ThreePointArc((-1.341640786, -3), (-1.799302724, -4.250096987), (-1.272792206, -5.472792206))
            ThreePointArc((-1.272792206, -5.472792206), (-1.272792206, -6.250609665), (-2.050609665, -6.250609665))
            ThreePointArc((-2.050609665, -6.250609665), (-2.853462499, -4.717447359), (-2.640075756, -3))
            Line((-2.640075756, -3), (-7, -3))
            Line((-7, -3), (-7, -18))
            Line((-7, -18), (-2.640075756, -18))
            ThreePointArc((-2.640075756, -18), (-2.853462499, -16.282552641), (-2.050609665, -14.749390335))
            ThreePointArc((-2.050609665, -14.749390335), (-1.272792206, -14.749390335), (-1.272792206, -15.527207794))
            ThreePointArc((-1.272792206, -15.527207794), (-1.799302724, -16.749903013), (-1.341640786, -18))
        make_face(mode=Mode.SUBTRACT)
    extrude(amount=MEMBER_1_4_DEPTH)

    # Member 1 4 end butt 1
    split(bisect_by=Plane(origin=(199.25, 1118.5, 0), x_dir=(1, 0, 0), z_dir=(0, -1, 0)), keep=Keep.TOP)

    # Member 1 4 end butt 2
    split(bisect_by=Plane(origin=(199.25, -1118.5, 0), x_dir=(-1, 0, 0), z_dir=(0, 1, 0)), keep=Keep.TOP)


with BuildPart() as body_5:
    # 草图2 → 凸台-拉伸1 (new body)
    with BuildSketch(Plane.XY.offset(9).offset(EXTRUDE_START)):
        Rectangle(SKETCH_2_W, SKETCH_2_H)
    extrude(amount=-EXTRUDE_1_DEPTH)


solid = Compound([part.part, body_2.part, body_3.part, body_4.part, body_5.part])
